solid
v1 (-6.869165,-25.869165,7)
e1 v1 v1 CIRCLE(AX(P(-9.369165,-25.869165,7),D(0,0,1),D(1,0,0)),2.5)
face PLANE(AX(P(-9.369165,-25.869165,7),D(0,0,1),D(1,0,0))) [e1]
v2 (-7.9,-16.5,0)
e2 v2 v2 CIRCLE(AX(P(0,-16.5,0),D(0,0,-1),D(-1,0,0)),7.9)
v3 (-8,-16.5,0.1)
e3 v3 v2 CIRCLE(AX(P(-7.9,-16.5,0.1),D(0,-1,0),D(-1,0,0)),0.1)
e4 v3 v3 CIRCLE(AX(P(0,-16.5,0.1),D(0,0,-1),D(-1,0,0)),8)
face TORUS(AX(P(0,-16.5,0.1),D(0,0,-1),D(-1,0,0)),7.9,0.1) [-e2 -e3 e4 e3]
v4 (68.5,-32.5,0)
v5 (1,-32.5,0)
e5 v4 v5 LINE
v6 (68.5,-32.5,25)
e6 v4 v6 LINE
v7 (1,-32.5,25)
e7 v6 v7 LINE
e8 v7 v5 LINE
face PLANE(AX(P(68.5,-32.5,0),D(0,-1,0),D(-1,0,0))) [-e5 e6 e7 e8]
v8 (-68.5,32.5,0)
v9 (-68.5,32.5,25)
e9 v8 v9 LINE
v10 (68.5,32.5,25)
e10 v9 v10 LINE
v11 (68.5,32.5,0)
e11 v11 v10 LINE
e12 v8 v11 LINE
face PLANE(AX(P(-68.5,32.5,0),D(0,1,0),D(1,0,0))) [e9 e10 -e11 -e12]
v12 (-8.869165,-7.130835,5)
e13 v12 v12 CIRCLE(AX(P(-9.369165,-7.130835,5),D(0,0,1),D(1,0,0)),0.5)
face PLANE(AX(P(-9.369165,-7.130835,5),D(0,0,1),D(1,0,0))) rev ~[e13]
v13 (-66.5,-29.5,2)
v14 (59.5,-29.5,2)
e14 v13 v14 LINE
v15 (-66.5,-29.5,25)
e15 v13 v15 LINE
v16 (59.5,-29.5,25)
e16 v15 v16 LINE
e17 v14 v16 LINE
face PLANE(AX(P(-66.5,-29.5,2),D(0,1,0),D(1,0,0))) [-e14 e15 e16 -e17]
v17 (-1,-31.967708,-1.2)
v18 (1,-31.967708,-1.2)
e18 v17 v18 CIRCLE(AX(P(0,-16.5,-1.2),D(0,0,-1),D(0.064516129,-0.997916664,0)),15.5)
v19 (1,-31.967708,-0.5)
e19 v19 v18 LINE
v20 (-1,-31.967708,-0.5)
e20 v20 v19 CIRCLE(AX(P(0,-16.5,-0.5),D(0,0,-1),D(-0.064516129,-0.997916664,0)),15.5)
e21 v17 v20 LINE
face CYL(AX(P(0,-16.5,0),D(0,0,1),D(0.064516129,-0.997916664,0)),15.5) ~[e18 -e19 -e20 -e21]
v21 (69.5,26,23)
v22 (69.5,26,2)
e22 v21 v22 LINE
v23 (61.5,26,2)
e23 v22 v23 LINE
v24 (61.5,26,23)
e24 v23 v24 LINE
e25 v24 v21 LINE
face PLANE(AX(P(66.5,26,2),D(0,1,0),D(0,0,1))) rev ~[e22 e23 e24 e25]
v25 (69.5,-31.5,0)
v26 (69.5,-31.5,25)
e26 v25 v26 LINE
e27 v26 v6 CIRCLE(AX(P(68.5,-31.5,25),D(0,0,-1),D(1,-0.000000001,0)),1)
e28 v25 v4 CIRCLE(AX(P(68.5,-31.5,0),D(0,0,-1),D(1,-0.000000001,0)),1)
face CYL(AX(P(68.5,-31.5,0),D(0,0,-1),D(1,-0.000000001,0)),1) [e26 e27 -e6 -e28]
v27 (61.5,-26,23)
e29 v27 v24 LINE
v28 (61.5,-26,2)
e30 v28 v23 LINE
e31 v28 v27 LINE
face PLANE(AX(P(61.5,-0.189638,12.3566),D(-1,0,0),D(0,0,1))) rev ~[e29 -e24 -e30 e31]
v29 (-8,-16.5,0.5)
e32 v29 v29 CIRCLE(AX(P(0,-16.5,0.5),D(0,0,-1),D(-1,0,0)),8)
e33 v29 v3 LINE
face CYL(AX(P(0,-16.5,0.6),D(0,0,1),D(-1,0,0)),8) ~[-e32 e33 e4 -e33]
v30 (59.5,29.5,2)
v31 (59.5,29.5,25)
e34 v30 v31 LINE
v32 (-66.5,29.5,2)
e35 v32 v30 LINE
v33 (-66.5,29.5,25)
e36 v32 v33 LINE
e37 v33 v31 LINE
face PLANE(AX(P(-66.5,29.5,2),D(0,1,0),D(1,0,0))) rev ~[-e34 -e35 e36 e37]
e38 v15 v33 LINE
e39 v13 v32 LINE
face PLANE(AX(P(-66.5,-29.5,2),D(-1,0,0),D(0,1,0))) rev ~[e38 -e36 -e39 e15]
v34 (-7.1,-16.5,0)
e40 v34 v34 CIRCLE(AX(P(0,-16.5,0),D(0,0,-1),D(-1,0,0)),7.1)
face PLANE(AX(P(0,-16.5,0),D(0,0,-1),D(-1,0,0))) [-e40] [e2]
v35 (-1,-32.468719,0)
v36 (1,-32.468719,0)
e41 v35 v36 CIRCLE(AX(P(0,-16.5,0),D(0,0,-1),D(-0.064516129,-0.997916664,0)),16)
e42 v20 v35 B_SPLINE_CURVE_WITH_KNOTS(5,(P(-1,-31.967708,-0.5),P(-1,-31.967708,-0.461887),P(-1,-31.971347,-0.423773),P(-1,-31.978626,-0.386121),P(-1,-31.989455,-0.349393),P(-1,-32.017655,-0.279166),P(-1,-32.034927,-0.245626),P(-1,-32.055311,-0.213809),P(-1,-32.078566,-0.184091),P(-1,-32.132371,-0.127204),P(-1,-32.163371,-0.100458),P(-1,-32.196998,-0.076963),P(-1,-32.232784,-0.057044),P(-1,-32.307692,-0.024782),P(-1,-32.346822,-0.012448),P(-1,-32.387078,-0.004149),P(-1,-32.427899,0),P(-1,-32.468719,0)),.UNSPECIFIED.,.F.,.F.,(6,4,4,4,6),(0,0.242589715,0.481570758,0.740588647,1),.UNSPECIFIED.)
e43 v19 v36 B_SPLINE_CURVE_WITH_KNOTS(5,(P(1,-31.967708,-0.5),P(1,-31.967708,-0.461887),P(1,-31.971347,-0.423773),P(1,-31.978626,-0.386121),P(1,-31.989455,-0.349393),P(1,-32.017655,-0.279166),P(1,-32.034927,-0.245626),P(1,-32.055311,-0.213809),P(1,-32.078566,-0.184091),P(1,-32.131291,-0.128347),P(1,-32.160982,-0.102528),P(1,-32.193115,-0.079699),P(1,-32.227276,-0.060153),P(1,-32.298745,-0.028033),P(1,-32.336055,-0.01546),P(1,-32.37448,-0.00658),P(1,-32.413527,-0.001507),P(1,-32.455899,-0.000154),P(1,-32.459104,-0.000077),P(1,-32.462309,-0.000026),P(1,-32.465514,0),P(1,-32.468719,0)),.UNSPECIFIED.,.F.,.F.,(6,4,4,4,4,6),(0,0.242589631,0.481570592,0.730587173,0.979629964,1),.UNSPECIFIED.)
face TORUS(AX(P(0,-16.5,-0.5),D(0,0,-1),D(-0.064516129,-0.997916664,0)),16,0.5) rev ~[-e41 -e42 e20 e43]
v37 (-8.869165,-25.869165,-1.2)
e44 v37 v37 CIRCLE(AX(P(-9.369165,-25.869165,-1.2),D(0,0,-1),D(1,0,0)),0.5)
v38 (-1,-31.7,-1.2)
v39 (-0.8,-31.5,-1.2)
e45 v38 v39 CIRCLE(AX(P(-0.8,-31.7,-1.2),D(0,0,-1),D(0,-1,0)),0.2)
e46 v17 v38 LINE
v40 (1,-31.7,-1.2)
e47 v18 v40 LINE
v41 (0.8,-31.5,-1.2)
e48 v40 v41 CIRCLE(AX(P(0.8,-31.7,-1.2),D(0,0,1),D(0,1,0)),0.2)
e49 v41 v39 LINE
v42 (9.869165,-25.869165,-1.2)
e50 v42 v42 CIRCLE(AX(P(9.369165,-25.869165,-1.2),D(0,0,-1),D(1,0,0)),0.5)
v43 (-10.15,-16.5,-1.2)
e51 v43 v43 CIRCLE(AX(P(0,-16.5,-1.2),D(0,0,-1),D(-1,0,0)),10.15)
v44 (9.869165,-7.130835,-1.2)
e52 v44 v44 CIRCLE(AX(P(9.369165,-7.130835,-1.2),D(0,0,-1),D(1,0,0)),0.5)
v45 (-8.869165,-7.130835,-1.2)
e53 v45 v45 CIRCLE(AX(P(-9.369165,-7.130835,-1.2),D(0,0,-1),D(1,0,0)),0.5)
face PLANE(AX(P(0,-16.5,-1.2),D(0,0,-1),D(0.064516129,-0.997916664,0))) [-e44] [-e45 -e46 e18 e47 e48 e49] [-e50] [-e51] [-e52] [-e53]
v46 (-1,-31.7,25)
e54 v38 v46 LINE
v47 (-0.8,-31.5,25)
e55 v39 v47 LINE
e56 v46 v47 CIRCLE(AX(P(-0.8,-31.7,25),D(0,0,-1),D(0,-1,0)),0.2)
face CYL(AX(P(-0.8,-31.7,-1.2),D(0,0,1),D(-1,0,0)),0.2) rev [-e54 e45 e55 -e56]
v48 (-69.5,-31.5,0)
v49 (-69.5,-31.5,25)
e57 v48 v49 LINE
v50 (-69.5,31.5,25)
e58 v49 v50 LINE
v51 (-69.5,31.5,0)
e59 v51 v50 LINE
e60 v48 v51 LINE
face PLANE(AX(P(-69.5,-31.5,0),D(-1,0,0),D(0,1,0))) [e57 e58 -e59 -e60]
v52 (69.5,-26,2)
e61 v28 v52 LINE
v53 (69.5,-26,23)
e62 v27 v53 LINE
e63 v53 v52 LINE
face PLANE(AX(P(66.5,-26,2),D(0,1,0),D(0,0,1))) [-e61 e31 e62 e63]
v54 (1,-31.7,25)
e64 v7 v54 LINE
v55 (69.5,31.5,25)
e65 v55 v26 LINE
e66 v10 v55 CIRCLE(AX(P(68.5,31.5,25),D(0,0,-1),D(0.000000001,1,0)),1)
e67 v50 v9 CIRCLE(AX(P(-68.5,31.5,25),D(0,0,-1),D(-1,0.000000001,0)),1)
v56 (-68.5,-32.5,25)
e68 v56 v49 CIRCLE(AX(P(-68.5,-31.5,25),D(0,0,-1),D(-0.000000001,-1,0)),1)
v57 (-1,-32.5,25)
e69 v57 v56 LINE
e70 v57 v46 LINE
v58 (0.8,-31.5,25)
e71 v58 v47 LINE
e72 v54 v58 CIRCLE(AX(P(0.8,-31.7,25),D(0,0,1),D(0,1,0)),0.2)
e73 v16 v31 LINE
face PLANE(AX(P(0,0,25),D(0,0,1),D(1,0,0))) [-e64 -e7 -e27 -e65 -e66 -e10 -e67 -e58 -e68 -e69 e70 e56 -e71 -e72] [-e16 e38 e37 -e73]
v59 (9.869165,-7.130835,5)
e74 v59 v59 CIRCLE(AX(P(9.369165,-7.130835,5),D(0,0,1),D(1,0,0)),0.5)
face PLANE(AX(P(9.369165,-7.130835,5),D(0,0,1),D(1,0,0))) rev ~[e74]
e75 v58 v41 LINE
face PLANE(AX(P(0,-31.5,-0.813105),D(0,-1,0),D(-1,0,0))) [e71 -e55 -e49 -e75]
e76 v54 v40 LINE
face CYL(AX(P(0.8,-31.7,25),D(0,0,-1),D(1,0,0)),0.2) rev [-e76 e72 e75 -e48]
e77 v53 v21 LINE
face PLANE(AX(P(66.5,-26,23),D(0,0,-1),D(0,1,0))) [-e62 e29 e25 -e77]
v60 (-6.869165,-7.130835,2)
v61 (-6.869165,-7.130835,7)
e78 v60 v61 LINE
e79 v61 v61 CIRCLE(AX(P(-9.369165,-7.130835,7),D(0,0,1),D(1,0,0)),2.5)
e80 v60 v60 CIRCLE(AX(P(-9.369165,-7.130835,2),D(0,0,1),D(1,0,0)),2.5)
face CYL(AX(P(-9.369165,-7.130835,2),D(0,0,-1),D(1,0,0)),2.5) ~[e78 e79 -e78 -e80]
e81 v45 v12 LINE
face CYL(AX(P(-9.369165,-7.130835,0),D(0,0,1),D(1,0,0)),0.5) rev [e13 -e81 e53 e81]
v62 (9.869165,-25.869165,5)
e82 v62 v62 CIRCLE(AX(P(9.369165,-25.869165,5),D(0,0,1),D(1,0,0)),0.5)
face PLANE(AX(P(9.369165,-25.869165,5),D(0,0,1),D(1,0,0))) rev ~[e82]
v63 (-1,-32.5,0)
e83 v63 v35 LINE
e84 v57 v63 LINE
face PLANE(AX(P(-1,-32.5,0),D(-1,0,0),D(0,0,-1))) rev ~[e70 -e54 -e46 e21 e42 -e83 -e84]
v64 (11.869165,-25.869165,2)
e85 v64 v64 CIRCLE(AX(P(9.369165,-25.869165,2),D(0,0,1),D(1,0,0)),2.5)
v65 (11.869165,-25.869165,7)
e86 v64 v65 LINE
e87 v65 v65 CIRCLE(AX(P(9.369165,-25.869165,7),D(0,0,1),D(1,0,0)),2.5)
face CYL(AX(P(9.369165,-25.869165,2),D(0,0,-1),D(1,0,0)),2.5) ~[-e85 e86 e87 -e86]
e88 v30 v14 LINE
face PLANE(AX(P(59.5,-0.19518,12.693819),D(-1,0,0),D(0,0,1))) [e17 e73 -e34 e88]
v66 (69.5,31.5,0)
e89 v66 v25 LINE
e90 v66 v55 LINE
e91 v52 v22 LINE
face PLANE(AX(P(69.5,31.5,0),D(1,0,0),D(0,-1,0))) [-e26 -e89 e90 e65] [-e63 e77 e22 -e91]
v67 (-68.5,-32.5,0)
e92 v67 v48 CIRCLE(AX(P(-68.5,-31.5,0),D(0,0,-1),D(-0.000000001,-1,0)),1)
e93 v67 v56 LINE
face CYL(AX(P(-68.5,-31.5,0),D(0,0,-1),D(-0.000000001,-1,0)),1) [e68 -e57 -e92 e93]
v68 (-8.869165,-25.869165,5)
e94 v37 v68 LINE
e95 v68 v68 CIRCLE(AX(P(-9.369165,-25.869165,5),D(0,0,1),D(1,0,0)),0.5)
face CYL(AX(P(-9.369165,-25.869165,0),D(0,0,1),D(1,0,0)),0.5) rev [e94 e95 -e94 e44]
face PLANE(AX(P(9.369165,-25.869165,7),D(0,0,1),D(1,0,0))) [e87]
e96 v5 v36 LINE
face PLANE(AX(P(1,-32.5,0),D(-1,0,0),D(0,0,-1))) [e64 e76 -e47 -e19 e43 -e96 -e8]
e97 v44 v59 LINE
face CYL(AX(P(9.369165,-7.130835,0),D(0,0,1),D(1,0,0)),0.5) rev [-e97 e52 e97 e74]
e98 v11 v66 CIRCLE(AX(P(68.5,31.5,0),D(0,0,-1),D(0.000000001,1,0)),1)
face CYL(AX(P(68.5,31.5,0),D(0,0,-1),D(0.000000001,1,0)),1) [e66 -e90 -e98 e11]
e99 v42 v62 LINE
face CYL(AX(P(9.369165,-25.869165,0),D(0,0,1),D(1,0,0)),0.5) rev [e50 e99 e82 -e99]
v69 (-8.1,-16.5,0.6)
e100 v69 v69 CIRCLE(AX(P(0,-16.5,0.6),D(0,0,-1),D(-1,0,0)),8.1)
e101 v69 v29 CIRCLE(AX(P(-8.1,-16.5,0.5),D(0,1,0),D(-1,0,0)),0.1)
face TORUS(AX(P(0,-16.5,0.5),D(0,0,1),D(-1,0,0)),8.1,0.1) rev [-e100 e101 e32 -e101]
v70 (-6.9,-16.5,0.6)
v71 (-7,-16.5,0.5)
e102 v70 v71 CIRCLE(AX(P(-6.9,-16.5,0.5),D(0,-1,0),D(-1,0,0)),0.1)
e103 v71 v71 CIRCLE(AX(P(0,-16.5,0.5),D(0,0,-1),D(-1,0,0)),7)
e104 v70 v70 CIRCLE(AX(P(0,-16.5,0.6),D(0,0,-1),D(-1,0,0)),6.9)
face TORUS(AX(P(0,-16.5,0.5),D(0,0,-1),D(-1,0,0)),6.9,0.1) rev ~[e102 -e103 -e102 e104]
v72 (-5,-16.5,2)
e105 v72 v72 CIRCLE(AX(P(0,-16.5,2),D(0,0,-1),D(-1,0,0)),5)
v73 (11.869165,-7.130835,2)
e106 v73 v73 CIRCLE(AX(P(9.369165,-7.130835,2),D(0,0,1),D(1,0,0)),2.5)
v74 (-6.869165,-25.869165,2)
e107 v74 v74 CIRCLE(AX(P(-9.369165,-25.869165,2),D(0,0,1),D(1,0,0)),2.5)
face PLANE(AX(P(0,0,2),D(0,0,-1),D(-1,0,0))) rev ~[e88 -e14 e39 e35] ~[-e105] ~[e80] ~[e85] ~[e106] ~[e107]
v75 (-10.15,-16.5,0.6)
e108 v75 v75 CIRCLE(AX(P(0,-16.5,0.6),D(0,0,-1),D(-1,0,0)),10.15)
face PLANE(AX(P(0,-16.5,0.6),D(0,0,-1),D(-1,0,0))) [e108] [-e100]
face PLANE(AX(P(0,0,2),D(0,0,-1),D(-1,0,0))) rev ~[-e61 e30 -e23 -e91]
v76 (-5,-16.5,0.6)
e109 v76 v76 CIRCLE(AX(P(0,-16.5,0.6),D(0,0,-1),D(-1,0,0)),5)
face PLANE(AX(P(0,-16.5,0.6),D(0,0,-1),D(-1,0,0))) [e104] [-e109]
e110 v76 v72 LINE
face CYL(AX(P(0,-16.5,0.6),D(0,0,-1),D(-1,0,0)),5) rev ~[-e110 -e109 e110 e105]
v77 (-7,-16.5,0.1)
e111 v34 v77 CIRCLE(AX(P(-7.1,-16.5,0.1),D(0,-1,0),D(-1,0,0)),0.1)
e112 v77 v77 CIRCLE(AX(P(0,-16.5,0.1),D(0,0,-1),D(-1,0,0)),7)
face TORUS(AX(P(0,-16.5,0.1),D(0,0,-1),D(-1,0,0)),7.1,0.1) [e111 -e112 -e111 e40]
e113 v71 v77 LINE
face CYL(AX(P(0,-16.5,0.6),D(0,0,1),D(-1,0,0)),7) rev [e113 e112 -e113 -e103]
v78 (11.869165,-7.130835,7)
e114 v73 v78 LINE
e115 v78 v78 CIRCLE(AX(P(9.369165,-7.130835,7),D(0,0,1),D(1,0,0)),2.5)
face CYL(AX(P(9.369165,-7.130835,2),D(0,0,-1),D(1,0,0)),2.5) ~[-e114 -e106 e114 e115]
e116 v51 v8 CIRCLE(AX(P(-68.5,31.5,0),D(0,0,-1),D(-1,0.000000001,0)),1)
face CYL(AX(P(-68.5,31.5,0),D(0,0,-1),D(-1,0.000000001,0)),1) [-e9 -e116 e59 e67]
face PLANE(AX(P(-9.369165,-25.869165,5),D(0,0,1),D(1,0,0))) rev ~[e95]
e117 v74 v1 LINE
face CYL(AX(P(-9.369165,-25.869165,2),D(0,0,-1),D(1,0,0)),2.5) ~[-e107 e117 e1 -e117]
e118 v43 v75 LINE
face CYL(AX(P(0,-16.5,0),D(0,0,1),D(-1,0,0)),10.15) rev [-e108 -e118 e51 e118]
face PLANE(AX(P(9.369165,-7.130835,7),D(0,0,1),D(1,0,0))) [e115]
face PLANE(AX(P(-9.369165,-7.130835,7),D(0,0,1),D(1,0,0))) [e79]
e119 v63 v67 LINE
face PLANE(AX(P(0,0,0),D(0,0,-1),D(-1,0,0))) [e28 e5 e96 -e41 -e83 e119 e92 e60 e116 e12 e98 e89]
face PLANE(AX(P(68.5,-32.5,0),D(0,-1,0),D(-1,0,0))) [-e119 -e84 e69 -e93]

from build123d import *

# Parameters (mm, degrees)
BOSS_EXTRUDE1_DEPTH  = 25
SHELL1_T             = -2
SKETCH6_R            = 10.15
CUT_EXTRUDE3_DEPTH   = 0.6
SKETCH10_R           = 5
CUT_EXTRUDE4_DEPTH   = 81.509999379
SKETCH11_R           = 8
SKETCH11_R_2         = 7
BOSS_EXTRUDE5_DEPTH  = 0.6
SKETCH13_R           = 2.5
BOSS_EXTRUDE6_DEPTH  = 5
CUT_EXTRUDE5_START   = -2
SKETCH15_R           = 0.5
CUT_EXTRUDE5_DEPTH   = 77.806725601
SKETCH16_W           = 2
SKETCH16_H           = 58.164373892
CUT_EXTRUDE6_DEPTH   = 1
FILLET2_R            = 0.1
SKETCH17_R           = 15.5
SKETCH17_R_2         = 10.15
SKETCH17_R_3         = 0.5
BOSS_EXTRUDE7_DEPTH  = 1.2
SKETCH18_W           = 2
SKETCH18_H           = 1.626209188
CUT_EXTRUDE7_DEPTH   = 1
FILLET3_R            = 0.5
FILLET5_R            = 0.2
SKETCH21_W           = 135
SKETCH21_H           = 61
SKETCH21_W_2         = 133
SKETCH21_H_2         = 59
BOSS_EXTRUDE8_DEPTH  = 23
CUT_EXTRUDE8_REACH   = 146.922
SKETCH20_W           = 21
SKETCH20_H           = 52
SKETCH22_W           = 24.612361346
SKETCH22_H           = 60.541750826
SKETCH22_W_2         = 21
SKETCH22_H_2         = 52
BOSS_EXTRUDE9_DEPTH  = 7
SKETCH23_W           = 22.768158453
SKETCH23_H           = 54.342974227
BOSS_EXTRUDE12_DEPTH = 2


with BuildPart() as part:
    # Sketch1 → Boss-Extrude1 (new body)
    with BuildSketch(Plane.XY):
        with BuildLine():
            Line((-68.5, 32.5), (68.5, 32.5))
            ThreePointArc((68.5, 32.5), (69.207106781, 32.207106781), (69.5, 31.5))
            Line((69.5, 31.5), (69.5, -31.5))
            ThreePointArc((69.5, -31.5), (69.207106781, -32.207106781), (68.5, -32.5))
            Line((68.5, -32.5), (-68.5, -32.5))
            ThreePointArc((-68.5, -32.5), (-69.207106781, -32.207106781), (-69.5, -31.5))
            Line((-69.5, -31.5), (-69.5, 31.5))
            ThreePointArc((-69.5, 31.5), (-69.207106781, 32.207106781), (-68.5, 32.5))
        make_face()
    extrude(amount=BOSS_EXTRUDE1_DEPTH)

    # Shell1
    shell1_openings = [part.faces().sort_by_distance(p)[0] for p in [
        (0, 0, 25),
    ]]
    offset(amount=SHELL1_T, openings=shell1_openings, kind=Kind.INTERSECTION)

    # Sketch6 → Cut-Extrude3 (cut)
    with BuildSketch(Plane(origin=(0, 0, 0), x_dir=(-1, 0, 0), z_dir=(0, 0, -1))):
        with Locations((0, -16.5)):
            Circle(SKETCH6_R)
    extrude(amount=-CUT_EXTRUDE3_DEPTH, mode=Mode.SUBTRACT)

    # Sketch10 → Cut-Extrude4 (cut, through all)
    with BuildSketch(Plane(origin=(0, 0, 0.6), x_dir=(-1, 0, 0), z_dir=(0, 0, -1))):
        with Locations((0, -16.5)):
            Circle(SKETCH10_R)
    extrude(amount=-CUT_EXTRUDE4_DEPTH, mode=Mode.SUBTRACT)

    # Sketch11 → Boss-Extrude5 (add)
    with BuildSketch(Plane(origin=(0, 0, 0.6), x_dir=(-1, 0, 0), z_dir=(0, 0, -1))):
        with Locations((0, -16.5)):
            Circle(SKETCH11_R)
        with Locations((0, -16.5)):
            Circle(SKETCH11_R_2, mode=Mode.SUBTRACT)
    extrude(amount=BOSS_EXTRUDE5_DEPTH)

    # Sketch13 → Boss-Extrude6 (add)
    with BuildSketch(Plane.XY.offset(2)):
        with Locations((-9.369164851, -7.130835149)):
            Circle(SKETCH13_R)
        with Locations((9.369164851, -7.130835149)):
            Circle(SKETCH13_R)
        with Locations((9.369164851, -25.869164851)):
            Circle(SKETCH13_R)
        with Locations((-9.369164851, -25.869164851)):
            Circle(SKETCH13_R)
    extrude(amount=BOSS_EXTRUDE6_DEPTH)

    # Sketch15 → Cut-Extrude5 (cut, through all)
    with BuildSketch(Plane.XY.offset(7).offset(CUT_EXTRUDE5_START)):
        with Locations((9.369164851, -7.130835149)):
            Circle(SKETCH15_R)
        with Locations((-9.369164851, -7.130835149)):
            Circle(SKETCH15_R)
        with Locations((-9.369164851, -25.869164851)):
            Circle(SKETCH15_R)
        with Locations((9.369164851, -25.869164851)):
            Circle(SKETCH15_R)
    extrude(amount=-CUT_EXTRUDE5_DEPTH, mode=Mode.SUBTRACT)

    # Sketch16 → Cut-Extrude6 (cut)
    with BuildSketch(Plane(origin=(0, -32.5, 0), x_dir=(-1, 0, 0), z_dir=(0, -1, 0))):
        Rectangle(SKETCH16_W, SKETCH16_H)
    extrude(amount=-CUT_EXTRUDE6_DEPTH, mode=Mode.SUBTRACT)

    # Fillet2
    fillet2_edges = [part.edges().sort_by_distance(p)[0] for p in [
        (7, -16.5, 0.6),
        (8, -16.5, 0),
        (8, -16.5, 0.6),
        (7, -16.5, 0),
    ]]
    fillet(fillet2_edges, radius=FILLET2_R)

    # Sketch17 → Boss-Extrude7 (add)
    with BuildSketch(Plane(origin=(0, 0, 0), x_dir=(-1, 0, 0), z_dir=(0, 0, -1))):
        with Locations(Location((0, -16.5, 0), (0, 0, 266.300928937))):
            Circle(SKETCH17_R)
        with Locations((0, -16.5)):
            Circle(SKETCH17_R_2, mode=Mode.SUBTRACT)
        with Locations(Location((-9.369164851, -7.130835149, 0), (0, 0, 180))):
            Circle(SKETCH17_R_3, mode=Mode.SUBTRACT)
        with Locations(Location((9.369164851, -7.130835149, 0), (0, 0, 180))):
            Circle(SKETCH17_R_3, mode=Mode.SUBTRACT)
        with Locations(Location((9.369164851, -25.869164851, 0), (0, 0, 180))):
            Circle(SKETCH17_R_3, mode=Mode.SUBTRACT)
        with Locations(Location((-9.369164851, -25.869164851, 0), (0, 0, 180))):
            Circle(SKETCH17_R_3, mode=Mode.SUBTRACT)
    extrude(amount=BOSS_EXTRUDE7_DEPTH)

    # Sketch18 → Cut-Extrude7 (cut)
    with BuildSketch(Plane(origin=(0, -32.5, 0), x_dir=(-1, 0, 0), z_dir=(0, -1, 0))):
        with Locations((0, 0.813104594)):
            Rectangle(SKETCH18_W, SKETCH18_H)
    extrude(amount=-CUT_EXTRUDE7_DEPTH, mode=Mode.SUBTRACT)

    # Fillet3
    fillet3_edges = [part.edges().sort_by_distance(p)[0] for p in [
        (2.2125523635452282e-11, -1.0000000000000018, 0),
    ]]
    fillet(fillet3_edges, radius=FILLET3_R)

    # Fillet5
    fillet5_edges = [part.edges().sort_by_distance(p)[0] for p in [
        (1, -31.5, 11.9),
        (-1, -31.5, 11.9),
    ]]
    fillet(fillet5_edges, radius=FILLET5_R)

    # Sketch21 → Boss-Extrude8 (add)
    with BuildSketch(Plane.XY.offset(2)):
        Rectangle(SKETCH21_W, SKETCH21_H)
        Rectangle(SKETCH21_W_2, SKETCH21_H_2, mode=Mode.SUBTRACT)
    extrude(amount=BOSS_EXTRUDE8_DEPTH)

    # Sketch20 → Cut-Extrude8 (cut, up to next)
    with BuildSketch(Plane(origin=(69.5, 0, 0), x_dir=(0, 0, -1), z_dir=(1, 0, 0)), mode=Mode.PRIVATE) as cut_extrude8_sk1:
        with Locations((-12.5, 0)):
            Rectangle(SKETCH20_W, SKETCH20_H)
    cut_extrude8_tool1 = extrude(cut_extrude8_sk1.sketch, amount=-CUT_EXTRUDE8_REACH, mode=Mode.PRIVATE) & part.part
    add(cut_extrude8_tool1.solids().sort_by_distance((69.5, 0, 12.5))[0], mode=Mode.SUBTRACT)

    # Sketch22 → Boss-Extrude9 (add)
    with BuildSketch(Plane.ZY.offset(-66.5)):
        with Locations((12.693819327, -0.195179749)):
            Rectangle(SKETCH22_W, SKETCH22_H)
        with Locations((12.5, 0)):
            Rectangle(SKETCH22_W_2, SKETCH22_H_2, mode=Mode.SUBTRACT)
    extrude(amount=BOSS_EXTRUDE9_DEPTH)

    # Sketch23 → Boss-Extrude12 (add)
    with BuildSketch(Plane.ZY.offset(-59.5)):
        with Locations((12.356599504, -0.189637576)):
            Rectangle(SKETCH23_W, SKETCH23_H)
    extrude(amount=-BOSS_EXTRUDE12_DEPTH)


solid = part.part
